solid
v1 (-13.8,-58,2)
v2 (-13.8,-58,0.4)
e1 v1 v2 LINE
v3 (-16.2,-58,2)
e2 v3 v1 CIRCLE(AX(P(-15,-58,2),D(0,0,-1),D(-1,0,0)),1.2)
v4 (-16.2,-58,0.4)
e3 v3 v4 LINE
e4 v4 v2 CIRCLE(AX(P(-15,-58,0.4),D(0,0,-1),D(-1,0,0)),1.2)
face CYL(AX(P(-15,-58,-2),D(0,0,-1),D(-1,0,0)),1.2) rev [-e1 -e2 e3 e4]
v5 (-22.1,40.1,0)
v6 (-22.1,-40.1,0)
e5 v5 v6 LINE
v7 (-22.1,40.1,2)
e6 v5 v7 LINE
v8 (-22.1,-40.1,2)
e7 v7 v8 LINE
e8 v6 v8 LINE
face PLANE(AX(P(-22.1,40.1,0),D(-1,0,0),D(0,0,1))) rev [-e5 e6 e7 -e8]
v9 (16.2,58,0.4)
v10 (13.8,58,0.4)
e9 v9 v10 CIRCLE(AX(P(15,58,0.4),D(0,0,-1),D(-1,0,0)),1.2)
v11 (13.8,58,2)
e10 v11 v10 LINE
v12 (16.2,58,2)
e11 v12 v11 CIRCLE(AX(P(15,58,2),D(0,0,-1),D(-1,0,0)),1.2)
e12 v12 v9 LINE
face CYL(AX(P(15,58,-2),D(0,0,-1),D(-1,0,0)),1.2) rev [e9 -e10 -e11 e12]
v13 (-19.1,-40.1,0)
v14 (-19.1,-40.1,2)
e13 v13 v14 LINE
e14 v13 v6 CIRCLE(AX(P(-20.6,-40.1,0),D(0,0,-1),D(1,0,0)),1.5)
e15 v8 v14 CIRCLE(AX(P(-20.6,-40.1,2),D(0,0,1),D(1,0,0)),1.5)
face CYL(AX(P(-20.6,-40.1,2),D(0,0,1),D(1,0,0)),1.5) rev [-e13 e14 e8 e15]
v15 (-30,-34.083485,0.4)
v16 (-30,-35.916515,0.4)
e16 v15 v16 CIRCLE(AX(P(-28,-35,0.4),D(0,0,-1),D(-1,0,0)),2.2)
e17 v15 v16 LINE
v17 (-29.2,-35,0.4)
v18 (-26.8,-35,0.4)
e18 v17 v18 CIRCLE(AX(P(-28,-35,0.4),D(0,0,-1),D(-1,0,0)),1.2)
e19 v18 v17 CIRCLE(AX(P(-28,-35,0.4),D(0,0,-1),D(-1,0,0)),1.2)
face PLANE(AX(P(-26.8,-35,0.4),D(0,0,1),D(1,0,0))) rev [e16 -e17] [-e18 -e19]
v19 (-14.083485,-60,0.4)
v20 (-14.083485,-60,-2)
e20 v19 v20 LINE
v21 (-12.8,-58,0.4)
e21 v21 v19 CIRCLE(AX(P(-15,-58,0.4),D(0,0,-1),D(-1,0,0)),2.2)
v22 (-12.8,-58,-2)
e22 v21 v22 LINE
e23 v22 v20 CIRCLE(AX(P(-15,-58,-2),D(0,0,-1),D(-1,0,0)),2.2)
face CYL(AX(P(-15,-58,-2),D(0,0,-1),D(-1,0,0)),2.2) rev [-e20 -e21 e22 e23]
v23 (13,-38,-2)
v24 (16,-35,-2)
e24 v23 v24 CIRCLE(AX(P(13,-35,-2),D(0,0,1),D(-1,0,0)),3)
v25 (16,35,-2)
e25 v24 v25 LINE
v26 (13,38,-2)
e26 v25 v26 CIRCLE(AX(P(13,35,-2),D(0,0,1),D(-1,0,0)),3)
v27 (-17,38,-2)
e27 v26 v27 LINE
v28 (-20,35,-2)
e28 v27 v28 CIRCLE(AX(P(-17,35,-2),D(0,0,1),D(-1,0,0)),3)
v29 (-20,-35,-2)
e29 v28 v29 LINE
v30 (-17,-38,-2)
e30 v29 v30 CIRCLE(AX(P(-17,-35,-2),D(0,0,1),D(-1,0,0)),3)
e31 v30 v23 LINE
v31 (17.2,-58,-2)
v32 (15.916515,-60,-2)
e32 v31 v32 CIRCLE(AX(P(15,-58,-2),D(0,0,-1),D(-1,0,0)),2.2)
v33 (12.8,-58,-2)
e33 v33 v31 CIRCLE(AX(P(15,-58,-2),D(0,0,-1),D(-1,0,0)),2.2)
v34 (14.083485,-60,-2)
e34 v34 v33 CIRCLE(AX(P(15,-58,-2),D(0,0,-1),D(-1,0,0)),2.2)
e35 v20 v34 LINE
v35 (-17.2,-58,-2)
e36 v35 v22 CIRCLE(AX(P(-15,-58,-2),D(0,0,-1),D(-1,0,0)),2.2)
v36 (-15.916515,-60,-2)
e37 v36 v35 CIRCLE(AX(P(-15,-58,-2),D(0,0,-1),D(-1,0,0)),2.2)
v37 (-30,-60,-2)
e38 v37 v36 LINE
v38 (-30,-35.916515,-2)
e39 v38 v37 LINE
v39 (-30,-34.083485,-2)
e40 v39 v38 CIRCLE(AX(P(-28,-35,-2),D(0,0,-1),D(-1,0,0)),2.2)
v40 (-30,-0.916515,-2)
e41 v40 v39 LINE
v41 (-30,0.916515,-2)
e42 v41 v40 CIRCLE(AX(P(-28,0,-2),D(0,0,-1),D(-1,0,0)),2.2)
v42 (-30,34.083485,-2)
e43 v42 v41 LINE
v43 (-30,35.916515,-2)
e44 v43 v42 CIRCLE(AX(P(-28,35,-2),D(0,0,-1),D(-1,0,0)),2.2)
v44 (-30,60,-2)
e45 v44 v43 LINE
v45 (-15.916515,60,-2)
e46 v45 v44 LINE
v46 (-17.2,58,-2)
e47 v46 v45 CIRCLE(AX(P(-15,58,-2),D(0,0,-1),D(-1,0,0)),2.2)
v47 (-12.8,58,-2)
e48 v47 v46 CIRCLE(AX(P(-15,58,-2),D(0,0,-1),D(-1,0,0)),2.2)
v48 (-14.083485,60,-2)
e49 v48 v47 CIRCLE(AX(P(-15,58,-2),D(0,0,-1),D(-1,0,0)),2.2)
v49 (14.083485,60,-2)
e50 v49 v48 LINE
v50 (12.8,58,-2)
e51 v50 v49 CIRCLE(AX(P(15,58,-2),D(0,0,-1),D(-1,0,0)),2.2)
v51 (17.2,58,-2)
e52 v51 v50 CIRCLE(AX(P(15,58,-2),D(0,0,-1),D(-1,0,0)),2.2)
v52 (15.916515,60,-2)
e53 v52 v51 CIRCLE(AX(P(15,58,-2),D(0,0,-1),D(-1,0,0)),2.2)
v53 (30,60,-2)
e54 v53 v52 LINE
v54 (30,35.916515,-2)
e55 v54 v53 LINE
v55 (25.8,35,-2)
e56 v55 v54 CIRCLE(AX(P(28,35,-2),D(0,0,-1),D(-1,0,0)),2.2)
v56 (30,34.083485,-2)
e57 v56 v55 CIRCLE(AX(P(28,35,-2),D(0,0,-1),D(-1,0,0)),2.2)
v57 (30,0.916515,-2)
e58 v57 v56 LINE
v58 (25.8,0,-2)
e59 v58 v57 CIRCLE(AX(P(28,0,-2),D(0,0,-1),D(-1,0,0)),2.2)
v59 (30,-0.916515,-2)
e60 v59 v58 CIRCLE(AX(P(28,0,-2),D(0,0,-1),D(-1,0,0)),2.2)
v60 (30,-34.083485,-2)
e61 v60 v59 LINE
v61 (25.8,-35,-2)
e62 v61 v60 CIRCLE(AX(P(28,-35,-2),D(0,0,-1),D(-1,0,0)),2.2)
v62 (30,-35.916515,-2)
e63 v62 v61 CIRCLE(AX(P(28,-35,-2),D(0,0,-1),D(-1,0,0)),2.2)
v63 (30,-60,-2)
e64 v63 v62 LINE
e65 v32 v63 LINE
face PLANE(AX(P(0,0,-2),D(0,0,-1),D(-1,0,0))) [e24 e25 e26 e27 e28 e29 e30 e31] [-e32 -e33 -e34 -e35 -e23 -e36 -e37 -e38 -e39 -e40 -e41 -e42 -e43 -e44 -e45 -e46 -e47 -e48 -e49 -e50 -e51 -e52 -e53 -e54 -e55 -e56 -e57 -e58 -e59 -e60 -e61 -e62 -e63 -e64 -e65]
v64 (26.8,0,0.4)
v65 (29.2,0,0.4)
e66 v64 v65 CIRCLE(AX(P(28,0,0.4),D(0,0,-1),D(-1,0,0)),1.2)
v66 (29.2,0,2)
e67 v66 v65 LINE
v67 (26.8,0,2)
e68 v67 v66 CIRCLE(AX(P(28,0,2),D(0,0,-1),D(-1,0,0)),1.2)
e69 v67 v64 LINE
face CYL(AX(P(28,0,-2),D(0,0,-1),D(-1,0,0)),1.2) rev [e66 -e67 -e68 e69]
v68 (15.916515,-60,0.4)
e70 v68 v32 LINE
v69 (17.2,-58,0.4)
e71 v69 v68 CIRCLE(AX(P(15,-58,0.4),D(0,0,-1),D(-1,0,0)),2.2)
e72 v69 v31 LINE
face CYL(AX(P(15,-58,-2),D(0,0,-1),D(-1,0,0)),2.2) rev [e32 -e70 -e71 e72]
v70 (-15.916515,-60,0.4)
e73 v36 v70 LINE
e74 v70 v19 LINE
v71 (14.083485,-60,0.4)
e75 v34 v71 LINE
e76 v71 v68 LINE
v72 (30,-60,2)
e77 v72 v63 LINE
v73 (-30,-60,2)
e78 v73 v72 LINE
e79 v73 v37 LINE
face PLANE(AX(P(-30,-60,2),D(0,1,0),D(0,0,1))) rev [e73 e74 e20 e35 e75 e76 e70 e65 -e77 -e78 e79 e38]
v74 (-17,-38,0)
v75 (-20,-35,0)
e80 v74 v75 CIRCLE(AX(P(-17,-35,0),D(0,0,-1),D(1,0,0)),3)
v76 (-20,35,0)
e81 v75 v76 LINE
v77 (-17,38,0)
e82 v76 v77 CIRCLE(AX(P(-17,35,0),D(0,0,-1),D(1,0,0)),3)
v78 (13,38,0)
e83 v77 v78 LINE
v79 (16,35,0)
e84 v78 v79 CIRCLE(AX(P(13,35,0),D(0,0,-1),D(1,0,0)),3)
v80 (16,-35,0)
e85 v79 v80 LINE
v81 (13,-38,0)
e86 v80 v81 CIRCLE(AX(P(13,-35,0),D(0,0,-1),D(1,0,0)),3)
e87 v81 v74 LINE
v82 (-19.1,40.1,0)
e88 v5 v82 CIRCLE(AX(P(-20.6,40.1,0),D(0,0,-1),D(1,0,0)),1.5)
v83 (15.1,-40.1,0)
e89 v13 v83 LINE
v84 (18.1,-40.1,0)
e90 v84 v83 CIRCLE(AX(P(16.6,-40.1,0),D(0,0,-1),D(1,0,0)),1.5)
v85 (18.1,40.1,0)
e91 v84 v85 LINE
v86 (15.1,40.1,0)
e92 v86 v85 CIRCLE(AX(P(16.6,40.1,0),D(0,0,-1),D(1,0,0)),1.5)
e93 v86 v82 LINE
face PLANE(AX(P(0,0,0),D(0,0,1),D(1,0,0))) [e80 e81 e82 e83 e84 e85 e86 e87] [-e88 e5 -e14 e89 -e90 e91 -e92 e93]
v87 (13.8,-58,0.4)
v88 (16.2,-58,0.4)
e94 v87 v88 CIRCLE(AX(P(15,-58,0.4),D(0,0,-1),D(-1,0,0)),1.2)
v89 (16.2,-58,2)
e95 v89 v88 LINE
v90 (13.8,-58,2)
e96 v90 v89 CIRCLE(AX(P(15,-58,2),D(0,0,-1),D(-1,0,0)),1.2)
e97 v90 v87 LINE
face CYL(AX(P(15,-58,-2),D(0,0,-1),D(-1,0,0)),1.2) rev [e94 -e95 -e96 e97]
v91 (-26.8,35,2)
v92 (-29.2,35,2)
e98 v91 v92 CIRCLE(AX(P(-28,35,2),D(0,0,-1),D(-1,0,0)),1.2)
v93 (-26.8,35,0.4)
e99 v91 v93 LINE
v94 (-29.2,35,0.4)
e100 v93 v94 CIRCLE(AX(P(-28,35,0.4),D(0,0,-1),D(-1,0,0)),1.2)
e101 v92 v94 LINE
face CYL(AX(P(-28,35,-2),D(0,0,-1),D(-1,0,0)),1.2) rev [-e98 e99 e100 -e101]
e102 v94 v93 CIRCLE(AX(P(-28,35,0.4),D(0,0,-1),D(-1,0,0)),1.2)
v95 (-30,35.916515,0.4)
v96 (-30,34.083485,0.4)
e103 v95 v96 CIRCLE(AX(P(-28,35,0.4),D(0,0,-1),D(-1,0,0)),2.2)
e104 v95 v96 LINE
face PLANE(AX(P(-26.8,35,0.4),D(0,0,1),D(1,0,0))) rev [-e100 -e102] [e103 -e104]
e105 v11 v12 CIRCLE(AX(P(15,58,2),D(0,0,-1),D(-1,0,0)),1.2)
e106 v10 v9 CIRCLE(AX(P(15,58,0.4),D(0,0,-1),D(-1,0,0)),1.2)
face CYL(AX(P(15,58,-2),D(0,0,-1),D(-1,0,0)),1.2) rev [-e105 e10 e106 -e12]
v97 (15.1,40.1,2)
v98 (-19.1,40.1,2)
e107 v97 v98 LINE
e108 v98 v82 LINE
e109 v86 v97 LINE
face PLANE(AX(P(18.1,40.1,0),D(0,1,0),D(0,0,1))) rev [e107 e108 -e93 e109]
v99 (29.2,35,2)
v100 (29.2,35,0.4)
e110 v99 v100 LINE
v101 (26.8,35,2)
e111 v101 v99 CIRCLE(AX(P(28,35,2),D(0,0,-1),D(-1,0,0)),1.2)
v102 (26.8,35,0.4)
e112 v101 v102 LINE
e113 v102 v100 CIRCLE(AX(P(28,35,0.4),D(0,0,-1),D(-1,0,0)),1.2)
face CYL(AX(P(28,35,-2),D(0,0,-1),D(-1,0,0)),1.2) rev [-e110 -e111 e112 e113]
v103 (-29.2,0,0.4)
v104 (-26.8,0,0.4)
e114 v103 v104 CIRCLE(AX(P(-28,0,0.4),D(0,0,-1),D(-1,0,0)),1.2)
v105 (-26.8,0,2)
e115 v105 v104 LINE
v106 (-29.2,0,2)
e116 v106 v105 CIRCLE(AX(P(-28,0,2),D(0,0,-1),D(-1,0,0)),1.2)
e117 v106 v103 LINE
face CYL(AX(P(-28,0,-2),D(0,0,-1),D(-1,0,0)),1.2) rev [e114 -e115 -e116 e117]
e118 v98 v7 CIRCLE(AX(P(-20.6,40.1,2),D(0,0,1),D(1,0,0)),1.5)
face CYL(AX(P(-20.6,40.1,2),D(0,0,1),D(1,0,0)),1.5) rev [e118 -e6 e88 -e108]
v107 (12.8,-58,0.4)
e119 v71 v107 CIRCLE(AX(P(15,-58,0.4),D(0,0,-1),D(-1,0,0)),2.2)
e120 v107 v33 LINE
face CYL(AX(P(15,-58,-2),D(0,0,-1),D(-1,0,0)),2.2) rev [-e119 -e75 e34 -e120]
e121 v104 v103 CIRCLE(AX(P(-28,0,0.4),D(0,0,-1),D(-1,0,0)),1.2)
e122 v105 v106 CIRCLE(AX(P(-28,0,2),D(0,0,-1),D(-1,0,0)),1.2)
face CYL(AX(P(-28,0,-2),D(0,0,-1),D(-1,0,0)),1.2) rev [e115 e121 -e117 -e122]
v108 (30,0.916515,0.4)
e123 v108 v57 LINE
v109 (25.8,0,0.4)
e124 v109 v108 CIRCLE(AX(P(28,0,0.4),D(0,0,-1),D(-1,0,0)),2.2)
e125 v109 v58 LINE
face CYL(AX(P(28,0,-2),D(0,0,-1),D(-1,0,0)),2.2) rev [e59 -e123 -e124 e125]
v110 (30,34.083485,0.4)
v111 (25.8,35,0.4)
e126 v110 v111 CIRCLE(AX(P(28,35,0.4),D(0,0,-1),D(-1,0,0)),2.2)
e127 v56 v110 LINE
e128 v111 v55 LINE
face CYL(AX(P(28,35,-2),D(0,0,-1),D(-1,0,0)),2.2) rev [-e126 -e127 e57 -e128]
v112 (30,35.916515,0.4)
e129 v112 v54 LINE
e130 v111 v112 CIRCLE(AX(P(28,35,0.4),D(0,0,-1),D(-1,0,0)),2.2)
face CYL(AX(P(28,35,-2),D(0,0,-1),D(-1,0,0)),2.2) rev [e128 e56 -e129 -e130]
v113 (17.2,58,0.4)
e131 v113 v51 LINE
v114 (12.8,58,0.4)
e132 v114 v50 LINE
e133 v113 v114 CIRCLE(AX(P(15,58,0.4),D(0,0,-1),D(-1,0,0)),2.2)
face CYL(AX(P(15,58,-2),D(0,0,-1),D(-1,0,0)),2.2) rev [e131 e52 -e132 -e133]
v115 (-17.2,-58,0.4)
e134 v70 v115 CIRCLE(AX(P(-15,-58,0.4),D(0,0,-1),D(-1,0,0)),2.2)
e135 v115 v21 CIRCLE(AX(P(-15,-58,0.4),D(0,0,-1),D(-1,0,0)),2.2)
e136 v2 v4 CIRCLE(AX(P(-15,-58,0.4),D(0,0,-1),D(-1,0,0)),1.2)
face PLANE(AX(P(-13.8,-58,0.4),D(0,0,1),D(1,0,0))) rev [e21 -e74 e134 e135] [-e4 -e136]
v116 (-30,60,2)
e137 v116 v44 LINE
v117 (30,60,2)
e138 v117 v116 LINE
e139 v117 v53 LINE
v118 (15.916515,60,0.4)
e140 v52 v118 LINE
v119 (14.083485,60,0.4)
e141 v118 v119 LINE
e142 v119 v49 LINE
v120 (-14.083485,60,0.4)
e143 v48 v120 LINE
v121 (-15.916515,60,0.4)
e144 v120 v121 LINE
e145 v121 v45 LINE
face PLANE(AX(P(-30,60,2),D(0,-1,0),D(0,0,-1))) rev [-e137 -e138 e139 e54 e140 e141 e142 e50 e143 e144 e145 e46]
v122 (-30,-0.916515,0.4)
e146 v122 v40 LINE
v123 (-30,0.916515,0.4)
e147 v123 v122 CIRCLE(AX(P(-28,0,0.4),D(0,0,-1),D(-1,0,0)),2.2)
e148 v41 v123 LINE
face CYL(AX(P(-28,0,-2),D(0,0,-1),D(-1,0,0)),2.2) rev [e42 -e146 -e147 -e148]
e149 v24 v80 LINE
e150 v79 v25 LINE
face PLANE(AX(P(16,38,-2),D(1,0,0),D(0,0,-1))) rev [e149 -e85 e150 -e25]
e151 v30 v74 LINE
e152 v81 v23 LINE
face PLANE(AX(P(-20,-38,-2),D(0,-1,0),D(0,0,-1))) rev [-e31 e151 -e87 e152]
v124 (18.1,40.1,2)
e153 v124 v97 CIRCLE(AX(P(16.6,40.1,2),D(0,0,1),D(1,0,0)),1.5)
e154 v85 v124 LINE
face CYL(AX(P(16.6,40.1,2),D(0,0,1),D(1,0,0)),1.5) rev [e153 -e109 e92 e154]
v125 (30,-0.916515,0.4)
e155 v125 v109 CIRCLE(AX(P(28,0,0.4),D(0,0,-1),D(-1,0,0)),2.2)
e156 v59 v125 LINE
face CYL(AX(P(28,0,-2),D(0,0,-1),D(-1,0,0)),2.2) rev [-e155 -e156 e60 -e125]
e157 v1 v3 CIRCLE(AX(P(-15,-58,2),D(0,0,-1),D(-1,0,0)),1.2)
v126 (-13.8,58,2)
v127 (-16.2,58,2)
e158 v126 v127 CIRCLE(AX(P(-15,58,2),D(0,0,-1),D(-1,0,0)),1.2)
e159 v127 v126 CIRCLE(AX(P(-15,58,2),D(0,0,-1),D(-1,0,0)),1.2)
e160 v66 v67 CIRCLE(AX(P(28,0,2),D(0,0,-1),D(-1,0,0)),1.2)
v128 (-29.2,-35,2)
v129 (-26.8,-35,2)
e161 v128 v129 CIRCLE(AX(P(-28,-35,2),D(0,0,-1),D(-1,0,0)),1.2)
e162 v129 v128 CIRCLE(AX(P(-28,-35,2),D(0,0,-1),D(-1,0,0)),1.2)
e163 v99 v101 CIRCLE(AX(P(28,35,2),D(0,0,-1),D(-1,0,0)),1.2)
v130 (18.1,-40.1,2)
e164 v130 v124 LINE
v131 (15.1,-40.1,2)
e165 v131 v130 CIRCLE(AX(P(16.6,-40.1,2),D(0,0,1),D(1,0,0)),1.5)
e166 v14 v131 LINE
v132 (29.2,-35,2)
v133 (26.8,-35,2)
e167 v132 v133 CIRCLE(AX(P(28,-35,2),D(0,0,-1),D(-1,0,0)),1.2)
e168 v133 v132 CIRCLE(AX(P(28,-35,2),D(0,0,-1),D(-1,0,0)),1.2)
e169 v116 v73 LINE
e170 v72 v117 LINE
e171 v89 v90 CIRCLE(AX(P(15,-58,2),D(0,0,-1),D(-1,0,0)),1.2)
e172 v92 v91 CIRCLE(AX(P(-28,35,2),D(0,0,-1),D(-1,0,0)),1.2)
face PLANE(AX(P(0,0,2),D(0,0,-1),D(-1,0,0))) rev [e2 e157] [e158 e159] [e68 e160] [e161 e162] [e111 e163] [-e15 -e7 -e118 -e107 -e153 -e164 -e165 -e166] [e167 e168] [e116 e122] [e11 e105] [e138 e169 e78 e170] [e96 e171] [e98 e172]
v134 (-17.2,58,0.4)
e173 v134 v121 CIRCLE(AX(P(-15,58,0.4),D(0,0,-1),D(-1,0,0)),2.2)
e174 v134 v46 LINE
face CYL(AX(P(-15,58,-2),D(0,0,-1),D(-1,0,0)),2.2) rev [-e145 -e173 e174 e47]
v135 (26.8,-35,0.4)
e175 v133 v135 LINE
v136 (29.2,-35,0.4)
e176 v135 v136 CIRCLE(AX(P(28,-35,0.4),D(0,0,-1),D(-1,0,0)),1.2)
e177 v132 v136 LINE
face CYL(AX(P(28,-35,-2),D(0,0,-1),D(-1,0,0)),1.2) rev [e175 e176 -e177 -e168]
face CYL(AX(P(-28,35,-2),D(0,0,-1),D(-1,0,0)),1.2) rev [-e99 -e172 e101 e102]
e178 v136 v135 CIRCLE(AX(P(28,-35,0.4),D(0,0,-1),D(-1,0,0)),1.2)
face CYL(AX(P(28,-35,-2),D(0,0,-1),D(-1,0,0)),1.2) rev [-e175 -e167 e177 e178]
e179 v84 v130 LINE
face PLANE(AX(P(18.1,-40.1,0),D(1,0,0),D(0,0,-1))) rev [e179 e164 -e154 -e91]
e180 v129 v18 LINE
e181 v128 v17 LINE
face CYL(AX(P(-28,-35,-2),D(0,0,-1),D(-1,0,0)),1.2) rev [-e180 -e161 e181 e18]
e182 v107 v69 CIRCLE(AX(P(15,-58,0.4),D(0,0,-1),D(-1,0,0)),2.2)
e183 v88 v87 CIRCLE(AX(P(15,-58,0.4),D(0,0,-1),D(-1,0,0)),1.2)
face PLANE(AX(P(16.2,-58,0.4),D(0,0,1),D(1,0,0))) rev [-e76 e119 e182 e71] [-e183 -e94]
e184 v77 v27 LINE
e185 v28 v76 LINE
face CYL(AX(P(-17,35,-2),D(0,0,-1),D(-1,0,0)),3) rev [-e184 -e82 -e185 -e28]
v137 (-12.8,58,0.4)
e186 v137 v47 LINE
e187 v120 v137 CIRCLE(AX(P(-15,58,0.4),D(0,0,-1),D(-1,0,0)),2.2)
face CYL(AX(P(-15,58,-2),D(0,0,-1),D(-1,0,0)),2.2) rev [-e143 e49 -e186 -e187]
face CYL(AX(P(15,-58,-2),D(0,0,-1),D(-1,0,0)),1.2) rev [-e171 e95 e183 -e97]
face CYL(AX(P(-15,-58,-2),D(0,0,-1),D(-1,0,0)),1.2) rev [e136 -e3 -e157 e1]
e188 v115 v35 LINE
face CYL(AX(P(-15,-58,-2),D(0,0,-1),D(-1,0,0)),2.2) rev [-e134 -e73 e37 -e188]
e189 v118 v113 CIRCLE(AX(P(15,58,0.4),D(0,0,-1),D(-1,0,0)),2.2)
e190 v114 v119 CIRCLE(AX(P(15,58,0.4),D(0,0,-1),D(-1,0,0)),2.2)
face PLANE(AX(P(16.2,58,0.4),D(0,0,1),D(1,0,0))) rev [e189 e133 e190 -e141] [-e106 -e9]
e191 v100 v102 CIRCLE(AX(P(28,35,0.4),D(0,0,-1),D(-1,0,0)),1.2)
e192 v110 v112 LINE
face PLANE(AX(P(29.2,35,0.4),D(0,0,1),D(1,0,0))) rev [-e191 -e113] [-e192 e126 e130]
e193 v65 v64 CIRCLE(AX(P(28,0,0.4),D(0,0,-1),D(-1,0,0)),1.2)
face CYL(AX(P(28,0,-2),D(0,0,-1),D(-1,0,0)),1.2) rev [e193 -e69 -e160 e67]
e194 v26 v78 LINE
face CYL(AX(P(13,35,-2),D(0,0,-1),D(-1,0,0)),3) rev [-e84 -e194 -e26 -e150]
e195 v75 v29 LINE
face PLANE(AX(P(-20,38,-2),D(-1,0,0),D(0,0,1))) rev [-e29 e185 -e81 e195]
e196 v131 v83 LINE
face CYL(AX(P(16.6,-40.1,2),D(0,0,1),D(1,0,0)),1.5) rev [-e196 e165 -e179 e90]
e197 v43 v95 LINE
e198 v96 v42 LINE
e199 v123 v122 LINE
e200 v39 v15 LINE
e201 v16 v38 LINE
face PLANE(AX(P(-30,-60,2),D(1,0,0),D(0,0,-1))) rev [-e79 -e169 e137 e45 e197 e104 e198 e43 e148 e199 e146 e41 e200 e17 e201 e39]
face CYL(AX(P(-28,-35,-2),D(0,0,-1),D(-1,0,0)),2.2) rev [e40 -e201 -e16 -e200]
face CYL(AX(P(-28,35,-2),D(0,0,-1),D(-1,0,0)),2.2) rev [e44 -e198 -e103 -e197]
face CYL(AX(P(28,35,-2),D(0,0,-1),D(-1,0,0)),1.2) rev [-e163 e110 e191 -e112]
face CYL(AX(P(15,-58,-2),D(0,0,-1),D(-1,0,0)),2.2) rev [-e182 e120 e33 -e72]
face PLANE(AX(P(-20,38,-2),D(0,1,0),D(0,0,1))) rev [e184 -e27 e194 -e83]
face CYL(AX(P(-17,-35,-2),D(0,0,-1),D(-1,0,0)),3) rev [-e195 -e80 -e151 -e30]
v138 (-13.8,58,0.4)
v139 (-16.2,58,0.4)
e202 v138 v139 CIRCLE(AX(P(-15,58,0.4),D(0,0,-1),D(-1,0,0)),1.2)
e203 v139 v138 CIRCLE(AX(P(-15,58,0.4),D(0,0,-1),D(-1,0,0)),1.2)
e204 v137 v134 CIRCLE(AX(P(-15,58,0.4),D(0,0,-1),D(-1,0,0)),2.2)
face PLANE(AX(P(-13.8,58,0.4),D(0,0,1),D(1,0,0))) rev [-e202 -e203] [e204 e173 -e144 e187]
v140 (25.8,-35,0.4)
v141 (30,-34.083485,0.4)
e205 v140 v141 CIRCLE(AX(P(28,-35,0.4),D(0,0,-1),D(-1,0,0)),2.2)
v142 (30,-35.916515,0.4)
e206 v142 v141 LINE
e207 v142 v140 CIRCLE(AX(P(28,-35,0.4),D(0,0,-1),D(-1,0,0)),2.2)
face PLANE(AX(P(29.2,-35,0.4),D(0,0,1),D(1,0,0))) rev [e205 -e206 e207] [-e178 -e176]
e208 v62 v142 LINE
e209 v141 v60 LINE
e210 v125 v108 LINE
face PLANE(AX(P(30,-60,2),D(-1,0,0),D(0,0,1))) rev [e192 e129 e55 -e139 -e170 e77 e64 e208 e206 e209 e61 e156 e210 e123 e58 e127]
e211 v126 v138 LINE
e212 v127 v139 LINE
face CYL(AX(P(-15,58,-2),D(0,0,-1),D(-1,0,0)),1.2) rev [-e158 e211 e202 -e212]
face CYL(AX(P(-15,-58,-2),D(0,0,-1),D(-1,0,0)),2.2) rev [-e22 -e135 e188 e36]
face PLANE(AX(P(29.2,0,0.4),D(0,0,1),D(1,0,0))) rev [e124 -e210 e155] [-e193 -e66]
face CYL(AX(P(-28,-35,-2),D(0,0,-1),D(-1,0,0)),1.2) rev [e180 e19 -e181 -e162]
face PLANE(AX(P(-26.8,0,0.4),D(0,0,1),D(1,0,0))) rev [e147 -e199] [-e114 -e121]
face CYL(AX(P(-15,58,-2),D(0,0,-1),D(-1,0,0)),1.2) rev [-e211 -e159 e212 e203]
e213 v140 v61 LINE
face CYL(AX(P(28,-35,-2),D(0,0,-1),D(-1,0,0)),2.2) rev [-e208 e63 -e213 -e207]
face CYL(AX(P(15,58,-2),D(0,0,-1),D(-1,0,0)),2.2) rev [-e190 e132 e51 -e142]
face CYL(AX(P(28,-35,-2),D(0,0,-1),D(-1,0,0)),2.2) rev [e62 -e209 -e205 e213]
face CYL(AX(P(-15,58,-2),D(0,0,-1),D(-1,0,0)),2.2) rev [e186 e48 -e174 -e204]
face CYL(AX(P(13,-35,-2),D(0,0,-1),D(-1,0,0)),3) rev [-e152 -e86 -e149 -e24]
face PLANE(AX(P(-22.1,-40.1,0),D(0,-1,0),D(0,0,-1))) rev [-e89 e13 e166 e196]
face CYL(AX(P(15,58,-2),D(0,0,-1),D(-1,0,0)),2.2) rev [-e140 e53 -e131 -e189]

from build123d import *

# Parameters (mm, degrees)
SKETCH_1_W                   = 60
SKETCH_1_H                   = 120
EXTRUDE_1_DEPTH              = 2
SKETCH_2_W                   = 36
SKETCH_2_H                   = 76
CUT_EXTRUDE_1_DEPTH          = 68.201190466
SKETCH_3_W                   = 40.2
SKETCH_3_H                   = 80.2
CUT_EXTRUDE_2_DEPTH          = 2
HOLE_WIZARD_3_0_3_1_D        = 3
HOLE_WIZARD_3_0_3_1_DEPTH    = 2
FILLET_1_R                   = 3
HOLE_WIZARD_M2_1_D           = 2.4
HOLE_WIZARD_M2_1_CBORE_D     = 4.4
HOLE_WIZARD_M2_1_CBORE_DEPTH = 2.4


with BuildPart() as part:
    # 草图1 → 凸台-拉伸1 (new, symmetric)
    with BuildSketch(Plane.XY):
        Rectangle(SKETCH_1_W, SKETCH_1_H)
    extrude(amount=EXTRUDE_1_DEPTH, both=True)

    # 草图2 → 切除-拉伸1 (cut, through all)
    with BuildSketch(Plane.XY.offset(2)):
        with Locations((-2, 0)):
            Rectangle(SKETCH_2_W, SKETCH_2_H)
    extrude(amount=-CUT_EXTRUDE_1_DEPTH, mode=Mode.SUBTRACT)

    # 草图3 → 切除-拉伸2 (cut)
    with BuildSketch(Plane.XY.offset(2)):
        with Locations((-2, 0)):
            Rectangle(SKETCH_3_W, SKETCH_3_H)
    extrude(amount=-CUT_EXTRUDE_2_DEPTH, mode=Mode.SUBTRACT)

    # Ø3.0 (3) 直径孔1
    with Locations(Plane.XY.offset(2)):
        with Locations((-20.6, 40.1), (16.6, 40.1), (16.6, -40.1), (-20.6, -40.1)):
            Hole(HOLE_WIZARD_3_0_3_1_D / 2, depth=HOLE_WIZARD_3_0_3_1_DEPTH)

    # 圆角1
    fillet_1_edges = [part.edges().sort_by_distance(p)[0] for p in [
        (-20, -38, -1),
        (-20, 38, -1),
        (16, 38, -1),
        (16, -38, -1),
    ]]
    fillet(fillet_1_edges, radius=FILLET_1_R)

    # M2 六角凹头螺钉的柱形沉头孔1 (through all)
    with Locations(Plane(origin=(0, 0, -2), x_dir=(1, 0, 0), z_dir=(0, 0, -1))):
        with Locations((-28, 0), (28, 0), (-15, -58), (15, -58), (-28, -35), (28, -35), (-28, 35), (28, 35), (-15, 58), (15, 58)):
            CounterBoreHole(HOLE_WIZARD_M2_1_D / 2, HOLE_WIZARD_M2_1_CBORE_D / 2, HOLE_WIZARD_M2_1_CBORE_DEPTH)


solid = part.part
